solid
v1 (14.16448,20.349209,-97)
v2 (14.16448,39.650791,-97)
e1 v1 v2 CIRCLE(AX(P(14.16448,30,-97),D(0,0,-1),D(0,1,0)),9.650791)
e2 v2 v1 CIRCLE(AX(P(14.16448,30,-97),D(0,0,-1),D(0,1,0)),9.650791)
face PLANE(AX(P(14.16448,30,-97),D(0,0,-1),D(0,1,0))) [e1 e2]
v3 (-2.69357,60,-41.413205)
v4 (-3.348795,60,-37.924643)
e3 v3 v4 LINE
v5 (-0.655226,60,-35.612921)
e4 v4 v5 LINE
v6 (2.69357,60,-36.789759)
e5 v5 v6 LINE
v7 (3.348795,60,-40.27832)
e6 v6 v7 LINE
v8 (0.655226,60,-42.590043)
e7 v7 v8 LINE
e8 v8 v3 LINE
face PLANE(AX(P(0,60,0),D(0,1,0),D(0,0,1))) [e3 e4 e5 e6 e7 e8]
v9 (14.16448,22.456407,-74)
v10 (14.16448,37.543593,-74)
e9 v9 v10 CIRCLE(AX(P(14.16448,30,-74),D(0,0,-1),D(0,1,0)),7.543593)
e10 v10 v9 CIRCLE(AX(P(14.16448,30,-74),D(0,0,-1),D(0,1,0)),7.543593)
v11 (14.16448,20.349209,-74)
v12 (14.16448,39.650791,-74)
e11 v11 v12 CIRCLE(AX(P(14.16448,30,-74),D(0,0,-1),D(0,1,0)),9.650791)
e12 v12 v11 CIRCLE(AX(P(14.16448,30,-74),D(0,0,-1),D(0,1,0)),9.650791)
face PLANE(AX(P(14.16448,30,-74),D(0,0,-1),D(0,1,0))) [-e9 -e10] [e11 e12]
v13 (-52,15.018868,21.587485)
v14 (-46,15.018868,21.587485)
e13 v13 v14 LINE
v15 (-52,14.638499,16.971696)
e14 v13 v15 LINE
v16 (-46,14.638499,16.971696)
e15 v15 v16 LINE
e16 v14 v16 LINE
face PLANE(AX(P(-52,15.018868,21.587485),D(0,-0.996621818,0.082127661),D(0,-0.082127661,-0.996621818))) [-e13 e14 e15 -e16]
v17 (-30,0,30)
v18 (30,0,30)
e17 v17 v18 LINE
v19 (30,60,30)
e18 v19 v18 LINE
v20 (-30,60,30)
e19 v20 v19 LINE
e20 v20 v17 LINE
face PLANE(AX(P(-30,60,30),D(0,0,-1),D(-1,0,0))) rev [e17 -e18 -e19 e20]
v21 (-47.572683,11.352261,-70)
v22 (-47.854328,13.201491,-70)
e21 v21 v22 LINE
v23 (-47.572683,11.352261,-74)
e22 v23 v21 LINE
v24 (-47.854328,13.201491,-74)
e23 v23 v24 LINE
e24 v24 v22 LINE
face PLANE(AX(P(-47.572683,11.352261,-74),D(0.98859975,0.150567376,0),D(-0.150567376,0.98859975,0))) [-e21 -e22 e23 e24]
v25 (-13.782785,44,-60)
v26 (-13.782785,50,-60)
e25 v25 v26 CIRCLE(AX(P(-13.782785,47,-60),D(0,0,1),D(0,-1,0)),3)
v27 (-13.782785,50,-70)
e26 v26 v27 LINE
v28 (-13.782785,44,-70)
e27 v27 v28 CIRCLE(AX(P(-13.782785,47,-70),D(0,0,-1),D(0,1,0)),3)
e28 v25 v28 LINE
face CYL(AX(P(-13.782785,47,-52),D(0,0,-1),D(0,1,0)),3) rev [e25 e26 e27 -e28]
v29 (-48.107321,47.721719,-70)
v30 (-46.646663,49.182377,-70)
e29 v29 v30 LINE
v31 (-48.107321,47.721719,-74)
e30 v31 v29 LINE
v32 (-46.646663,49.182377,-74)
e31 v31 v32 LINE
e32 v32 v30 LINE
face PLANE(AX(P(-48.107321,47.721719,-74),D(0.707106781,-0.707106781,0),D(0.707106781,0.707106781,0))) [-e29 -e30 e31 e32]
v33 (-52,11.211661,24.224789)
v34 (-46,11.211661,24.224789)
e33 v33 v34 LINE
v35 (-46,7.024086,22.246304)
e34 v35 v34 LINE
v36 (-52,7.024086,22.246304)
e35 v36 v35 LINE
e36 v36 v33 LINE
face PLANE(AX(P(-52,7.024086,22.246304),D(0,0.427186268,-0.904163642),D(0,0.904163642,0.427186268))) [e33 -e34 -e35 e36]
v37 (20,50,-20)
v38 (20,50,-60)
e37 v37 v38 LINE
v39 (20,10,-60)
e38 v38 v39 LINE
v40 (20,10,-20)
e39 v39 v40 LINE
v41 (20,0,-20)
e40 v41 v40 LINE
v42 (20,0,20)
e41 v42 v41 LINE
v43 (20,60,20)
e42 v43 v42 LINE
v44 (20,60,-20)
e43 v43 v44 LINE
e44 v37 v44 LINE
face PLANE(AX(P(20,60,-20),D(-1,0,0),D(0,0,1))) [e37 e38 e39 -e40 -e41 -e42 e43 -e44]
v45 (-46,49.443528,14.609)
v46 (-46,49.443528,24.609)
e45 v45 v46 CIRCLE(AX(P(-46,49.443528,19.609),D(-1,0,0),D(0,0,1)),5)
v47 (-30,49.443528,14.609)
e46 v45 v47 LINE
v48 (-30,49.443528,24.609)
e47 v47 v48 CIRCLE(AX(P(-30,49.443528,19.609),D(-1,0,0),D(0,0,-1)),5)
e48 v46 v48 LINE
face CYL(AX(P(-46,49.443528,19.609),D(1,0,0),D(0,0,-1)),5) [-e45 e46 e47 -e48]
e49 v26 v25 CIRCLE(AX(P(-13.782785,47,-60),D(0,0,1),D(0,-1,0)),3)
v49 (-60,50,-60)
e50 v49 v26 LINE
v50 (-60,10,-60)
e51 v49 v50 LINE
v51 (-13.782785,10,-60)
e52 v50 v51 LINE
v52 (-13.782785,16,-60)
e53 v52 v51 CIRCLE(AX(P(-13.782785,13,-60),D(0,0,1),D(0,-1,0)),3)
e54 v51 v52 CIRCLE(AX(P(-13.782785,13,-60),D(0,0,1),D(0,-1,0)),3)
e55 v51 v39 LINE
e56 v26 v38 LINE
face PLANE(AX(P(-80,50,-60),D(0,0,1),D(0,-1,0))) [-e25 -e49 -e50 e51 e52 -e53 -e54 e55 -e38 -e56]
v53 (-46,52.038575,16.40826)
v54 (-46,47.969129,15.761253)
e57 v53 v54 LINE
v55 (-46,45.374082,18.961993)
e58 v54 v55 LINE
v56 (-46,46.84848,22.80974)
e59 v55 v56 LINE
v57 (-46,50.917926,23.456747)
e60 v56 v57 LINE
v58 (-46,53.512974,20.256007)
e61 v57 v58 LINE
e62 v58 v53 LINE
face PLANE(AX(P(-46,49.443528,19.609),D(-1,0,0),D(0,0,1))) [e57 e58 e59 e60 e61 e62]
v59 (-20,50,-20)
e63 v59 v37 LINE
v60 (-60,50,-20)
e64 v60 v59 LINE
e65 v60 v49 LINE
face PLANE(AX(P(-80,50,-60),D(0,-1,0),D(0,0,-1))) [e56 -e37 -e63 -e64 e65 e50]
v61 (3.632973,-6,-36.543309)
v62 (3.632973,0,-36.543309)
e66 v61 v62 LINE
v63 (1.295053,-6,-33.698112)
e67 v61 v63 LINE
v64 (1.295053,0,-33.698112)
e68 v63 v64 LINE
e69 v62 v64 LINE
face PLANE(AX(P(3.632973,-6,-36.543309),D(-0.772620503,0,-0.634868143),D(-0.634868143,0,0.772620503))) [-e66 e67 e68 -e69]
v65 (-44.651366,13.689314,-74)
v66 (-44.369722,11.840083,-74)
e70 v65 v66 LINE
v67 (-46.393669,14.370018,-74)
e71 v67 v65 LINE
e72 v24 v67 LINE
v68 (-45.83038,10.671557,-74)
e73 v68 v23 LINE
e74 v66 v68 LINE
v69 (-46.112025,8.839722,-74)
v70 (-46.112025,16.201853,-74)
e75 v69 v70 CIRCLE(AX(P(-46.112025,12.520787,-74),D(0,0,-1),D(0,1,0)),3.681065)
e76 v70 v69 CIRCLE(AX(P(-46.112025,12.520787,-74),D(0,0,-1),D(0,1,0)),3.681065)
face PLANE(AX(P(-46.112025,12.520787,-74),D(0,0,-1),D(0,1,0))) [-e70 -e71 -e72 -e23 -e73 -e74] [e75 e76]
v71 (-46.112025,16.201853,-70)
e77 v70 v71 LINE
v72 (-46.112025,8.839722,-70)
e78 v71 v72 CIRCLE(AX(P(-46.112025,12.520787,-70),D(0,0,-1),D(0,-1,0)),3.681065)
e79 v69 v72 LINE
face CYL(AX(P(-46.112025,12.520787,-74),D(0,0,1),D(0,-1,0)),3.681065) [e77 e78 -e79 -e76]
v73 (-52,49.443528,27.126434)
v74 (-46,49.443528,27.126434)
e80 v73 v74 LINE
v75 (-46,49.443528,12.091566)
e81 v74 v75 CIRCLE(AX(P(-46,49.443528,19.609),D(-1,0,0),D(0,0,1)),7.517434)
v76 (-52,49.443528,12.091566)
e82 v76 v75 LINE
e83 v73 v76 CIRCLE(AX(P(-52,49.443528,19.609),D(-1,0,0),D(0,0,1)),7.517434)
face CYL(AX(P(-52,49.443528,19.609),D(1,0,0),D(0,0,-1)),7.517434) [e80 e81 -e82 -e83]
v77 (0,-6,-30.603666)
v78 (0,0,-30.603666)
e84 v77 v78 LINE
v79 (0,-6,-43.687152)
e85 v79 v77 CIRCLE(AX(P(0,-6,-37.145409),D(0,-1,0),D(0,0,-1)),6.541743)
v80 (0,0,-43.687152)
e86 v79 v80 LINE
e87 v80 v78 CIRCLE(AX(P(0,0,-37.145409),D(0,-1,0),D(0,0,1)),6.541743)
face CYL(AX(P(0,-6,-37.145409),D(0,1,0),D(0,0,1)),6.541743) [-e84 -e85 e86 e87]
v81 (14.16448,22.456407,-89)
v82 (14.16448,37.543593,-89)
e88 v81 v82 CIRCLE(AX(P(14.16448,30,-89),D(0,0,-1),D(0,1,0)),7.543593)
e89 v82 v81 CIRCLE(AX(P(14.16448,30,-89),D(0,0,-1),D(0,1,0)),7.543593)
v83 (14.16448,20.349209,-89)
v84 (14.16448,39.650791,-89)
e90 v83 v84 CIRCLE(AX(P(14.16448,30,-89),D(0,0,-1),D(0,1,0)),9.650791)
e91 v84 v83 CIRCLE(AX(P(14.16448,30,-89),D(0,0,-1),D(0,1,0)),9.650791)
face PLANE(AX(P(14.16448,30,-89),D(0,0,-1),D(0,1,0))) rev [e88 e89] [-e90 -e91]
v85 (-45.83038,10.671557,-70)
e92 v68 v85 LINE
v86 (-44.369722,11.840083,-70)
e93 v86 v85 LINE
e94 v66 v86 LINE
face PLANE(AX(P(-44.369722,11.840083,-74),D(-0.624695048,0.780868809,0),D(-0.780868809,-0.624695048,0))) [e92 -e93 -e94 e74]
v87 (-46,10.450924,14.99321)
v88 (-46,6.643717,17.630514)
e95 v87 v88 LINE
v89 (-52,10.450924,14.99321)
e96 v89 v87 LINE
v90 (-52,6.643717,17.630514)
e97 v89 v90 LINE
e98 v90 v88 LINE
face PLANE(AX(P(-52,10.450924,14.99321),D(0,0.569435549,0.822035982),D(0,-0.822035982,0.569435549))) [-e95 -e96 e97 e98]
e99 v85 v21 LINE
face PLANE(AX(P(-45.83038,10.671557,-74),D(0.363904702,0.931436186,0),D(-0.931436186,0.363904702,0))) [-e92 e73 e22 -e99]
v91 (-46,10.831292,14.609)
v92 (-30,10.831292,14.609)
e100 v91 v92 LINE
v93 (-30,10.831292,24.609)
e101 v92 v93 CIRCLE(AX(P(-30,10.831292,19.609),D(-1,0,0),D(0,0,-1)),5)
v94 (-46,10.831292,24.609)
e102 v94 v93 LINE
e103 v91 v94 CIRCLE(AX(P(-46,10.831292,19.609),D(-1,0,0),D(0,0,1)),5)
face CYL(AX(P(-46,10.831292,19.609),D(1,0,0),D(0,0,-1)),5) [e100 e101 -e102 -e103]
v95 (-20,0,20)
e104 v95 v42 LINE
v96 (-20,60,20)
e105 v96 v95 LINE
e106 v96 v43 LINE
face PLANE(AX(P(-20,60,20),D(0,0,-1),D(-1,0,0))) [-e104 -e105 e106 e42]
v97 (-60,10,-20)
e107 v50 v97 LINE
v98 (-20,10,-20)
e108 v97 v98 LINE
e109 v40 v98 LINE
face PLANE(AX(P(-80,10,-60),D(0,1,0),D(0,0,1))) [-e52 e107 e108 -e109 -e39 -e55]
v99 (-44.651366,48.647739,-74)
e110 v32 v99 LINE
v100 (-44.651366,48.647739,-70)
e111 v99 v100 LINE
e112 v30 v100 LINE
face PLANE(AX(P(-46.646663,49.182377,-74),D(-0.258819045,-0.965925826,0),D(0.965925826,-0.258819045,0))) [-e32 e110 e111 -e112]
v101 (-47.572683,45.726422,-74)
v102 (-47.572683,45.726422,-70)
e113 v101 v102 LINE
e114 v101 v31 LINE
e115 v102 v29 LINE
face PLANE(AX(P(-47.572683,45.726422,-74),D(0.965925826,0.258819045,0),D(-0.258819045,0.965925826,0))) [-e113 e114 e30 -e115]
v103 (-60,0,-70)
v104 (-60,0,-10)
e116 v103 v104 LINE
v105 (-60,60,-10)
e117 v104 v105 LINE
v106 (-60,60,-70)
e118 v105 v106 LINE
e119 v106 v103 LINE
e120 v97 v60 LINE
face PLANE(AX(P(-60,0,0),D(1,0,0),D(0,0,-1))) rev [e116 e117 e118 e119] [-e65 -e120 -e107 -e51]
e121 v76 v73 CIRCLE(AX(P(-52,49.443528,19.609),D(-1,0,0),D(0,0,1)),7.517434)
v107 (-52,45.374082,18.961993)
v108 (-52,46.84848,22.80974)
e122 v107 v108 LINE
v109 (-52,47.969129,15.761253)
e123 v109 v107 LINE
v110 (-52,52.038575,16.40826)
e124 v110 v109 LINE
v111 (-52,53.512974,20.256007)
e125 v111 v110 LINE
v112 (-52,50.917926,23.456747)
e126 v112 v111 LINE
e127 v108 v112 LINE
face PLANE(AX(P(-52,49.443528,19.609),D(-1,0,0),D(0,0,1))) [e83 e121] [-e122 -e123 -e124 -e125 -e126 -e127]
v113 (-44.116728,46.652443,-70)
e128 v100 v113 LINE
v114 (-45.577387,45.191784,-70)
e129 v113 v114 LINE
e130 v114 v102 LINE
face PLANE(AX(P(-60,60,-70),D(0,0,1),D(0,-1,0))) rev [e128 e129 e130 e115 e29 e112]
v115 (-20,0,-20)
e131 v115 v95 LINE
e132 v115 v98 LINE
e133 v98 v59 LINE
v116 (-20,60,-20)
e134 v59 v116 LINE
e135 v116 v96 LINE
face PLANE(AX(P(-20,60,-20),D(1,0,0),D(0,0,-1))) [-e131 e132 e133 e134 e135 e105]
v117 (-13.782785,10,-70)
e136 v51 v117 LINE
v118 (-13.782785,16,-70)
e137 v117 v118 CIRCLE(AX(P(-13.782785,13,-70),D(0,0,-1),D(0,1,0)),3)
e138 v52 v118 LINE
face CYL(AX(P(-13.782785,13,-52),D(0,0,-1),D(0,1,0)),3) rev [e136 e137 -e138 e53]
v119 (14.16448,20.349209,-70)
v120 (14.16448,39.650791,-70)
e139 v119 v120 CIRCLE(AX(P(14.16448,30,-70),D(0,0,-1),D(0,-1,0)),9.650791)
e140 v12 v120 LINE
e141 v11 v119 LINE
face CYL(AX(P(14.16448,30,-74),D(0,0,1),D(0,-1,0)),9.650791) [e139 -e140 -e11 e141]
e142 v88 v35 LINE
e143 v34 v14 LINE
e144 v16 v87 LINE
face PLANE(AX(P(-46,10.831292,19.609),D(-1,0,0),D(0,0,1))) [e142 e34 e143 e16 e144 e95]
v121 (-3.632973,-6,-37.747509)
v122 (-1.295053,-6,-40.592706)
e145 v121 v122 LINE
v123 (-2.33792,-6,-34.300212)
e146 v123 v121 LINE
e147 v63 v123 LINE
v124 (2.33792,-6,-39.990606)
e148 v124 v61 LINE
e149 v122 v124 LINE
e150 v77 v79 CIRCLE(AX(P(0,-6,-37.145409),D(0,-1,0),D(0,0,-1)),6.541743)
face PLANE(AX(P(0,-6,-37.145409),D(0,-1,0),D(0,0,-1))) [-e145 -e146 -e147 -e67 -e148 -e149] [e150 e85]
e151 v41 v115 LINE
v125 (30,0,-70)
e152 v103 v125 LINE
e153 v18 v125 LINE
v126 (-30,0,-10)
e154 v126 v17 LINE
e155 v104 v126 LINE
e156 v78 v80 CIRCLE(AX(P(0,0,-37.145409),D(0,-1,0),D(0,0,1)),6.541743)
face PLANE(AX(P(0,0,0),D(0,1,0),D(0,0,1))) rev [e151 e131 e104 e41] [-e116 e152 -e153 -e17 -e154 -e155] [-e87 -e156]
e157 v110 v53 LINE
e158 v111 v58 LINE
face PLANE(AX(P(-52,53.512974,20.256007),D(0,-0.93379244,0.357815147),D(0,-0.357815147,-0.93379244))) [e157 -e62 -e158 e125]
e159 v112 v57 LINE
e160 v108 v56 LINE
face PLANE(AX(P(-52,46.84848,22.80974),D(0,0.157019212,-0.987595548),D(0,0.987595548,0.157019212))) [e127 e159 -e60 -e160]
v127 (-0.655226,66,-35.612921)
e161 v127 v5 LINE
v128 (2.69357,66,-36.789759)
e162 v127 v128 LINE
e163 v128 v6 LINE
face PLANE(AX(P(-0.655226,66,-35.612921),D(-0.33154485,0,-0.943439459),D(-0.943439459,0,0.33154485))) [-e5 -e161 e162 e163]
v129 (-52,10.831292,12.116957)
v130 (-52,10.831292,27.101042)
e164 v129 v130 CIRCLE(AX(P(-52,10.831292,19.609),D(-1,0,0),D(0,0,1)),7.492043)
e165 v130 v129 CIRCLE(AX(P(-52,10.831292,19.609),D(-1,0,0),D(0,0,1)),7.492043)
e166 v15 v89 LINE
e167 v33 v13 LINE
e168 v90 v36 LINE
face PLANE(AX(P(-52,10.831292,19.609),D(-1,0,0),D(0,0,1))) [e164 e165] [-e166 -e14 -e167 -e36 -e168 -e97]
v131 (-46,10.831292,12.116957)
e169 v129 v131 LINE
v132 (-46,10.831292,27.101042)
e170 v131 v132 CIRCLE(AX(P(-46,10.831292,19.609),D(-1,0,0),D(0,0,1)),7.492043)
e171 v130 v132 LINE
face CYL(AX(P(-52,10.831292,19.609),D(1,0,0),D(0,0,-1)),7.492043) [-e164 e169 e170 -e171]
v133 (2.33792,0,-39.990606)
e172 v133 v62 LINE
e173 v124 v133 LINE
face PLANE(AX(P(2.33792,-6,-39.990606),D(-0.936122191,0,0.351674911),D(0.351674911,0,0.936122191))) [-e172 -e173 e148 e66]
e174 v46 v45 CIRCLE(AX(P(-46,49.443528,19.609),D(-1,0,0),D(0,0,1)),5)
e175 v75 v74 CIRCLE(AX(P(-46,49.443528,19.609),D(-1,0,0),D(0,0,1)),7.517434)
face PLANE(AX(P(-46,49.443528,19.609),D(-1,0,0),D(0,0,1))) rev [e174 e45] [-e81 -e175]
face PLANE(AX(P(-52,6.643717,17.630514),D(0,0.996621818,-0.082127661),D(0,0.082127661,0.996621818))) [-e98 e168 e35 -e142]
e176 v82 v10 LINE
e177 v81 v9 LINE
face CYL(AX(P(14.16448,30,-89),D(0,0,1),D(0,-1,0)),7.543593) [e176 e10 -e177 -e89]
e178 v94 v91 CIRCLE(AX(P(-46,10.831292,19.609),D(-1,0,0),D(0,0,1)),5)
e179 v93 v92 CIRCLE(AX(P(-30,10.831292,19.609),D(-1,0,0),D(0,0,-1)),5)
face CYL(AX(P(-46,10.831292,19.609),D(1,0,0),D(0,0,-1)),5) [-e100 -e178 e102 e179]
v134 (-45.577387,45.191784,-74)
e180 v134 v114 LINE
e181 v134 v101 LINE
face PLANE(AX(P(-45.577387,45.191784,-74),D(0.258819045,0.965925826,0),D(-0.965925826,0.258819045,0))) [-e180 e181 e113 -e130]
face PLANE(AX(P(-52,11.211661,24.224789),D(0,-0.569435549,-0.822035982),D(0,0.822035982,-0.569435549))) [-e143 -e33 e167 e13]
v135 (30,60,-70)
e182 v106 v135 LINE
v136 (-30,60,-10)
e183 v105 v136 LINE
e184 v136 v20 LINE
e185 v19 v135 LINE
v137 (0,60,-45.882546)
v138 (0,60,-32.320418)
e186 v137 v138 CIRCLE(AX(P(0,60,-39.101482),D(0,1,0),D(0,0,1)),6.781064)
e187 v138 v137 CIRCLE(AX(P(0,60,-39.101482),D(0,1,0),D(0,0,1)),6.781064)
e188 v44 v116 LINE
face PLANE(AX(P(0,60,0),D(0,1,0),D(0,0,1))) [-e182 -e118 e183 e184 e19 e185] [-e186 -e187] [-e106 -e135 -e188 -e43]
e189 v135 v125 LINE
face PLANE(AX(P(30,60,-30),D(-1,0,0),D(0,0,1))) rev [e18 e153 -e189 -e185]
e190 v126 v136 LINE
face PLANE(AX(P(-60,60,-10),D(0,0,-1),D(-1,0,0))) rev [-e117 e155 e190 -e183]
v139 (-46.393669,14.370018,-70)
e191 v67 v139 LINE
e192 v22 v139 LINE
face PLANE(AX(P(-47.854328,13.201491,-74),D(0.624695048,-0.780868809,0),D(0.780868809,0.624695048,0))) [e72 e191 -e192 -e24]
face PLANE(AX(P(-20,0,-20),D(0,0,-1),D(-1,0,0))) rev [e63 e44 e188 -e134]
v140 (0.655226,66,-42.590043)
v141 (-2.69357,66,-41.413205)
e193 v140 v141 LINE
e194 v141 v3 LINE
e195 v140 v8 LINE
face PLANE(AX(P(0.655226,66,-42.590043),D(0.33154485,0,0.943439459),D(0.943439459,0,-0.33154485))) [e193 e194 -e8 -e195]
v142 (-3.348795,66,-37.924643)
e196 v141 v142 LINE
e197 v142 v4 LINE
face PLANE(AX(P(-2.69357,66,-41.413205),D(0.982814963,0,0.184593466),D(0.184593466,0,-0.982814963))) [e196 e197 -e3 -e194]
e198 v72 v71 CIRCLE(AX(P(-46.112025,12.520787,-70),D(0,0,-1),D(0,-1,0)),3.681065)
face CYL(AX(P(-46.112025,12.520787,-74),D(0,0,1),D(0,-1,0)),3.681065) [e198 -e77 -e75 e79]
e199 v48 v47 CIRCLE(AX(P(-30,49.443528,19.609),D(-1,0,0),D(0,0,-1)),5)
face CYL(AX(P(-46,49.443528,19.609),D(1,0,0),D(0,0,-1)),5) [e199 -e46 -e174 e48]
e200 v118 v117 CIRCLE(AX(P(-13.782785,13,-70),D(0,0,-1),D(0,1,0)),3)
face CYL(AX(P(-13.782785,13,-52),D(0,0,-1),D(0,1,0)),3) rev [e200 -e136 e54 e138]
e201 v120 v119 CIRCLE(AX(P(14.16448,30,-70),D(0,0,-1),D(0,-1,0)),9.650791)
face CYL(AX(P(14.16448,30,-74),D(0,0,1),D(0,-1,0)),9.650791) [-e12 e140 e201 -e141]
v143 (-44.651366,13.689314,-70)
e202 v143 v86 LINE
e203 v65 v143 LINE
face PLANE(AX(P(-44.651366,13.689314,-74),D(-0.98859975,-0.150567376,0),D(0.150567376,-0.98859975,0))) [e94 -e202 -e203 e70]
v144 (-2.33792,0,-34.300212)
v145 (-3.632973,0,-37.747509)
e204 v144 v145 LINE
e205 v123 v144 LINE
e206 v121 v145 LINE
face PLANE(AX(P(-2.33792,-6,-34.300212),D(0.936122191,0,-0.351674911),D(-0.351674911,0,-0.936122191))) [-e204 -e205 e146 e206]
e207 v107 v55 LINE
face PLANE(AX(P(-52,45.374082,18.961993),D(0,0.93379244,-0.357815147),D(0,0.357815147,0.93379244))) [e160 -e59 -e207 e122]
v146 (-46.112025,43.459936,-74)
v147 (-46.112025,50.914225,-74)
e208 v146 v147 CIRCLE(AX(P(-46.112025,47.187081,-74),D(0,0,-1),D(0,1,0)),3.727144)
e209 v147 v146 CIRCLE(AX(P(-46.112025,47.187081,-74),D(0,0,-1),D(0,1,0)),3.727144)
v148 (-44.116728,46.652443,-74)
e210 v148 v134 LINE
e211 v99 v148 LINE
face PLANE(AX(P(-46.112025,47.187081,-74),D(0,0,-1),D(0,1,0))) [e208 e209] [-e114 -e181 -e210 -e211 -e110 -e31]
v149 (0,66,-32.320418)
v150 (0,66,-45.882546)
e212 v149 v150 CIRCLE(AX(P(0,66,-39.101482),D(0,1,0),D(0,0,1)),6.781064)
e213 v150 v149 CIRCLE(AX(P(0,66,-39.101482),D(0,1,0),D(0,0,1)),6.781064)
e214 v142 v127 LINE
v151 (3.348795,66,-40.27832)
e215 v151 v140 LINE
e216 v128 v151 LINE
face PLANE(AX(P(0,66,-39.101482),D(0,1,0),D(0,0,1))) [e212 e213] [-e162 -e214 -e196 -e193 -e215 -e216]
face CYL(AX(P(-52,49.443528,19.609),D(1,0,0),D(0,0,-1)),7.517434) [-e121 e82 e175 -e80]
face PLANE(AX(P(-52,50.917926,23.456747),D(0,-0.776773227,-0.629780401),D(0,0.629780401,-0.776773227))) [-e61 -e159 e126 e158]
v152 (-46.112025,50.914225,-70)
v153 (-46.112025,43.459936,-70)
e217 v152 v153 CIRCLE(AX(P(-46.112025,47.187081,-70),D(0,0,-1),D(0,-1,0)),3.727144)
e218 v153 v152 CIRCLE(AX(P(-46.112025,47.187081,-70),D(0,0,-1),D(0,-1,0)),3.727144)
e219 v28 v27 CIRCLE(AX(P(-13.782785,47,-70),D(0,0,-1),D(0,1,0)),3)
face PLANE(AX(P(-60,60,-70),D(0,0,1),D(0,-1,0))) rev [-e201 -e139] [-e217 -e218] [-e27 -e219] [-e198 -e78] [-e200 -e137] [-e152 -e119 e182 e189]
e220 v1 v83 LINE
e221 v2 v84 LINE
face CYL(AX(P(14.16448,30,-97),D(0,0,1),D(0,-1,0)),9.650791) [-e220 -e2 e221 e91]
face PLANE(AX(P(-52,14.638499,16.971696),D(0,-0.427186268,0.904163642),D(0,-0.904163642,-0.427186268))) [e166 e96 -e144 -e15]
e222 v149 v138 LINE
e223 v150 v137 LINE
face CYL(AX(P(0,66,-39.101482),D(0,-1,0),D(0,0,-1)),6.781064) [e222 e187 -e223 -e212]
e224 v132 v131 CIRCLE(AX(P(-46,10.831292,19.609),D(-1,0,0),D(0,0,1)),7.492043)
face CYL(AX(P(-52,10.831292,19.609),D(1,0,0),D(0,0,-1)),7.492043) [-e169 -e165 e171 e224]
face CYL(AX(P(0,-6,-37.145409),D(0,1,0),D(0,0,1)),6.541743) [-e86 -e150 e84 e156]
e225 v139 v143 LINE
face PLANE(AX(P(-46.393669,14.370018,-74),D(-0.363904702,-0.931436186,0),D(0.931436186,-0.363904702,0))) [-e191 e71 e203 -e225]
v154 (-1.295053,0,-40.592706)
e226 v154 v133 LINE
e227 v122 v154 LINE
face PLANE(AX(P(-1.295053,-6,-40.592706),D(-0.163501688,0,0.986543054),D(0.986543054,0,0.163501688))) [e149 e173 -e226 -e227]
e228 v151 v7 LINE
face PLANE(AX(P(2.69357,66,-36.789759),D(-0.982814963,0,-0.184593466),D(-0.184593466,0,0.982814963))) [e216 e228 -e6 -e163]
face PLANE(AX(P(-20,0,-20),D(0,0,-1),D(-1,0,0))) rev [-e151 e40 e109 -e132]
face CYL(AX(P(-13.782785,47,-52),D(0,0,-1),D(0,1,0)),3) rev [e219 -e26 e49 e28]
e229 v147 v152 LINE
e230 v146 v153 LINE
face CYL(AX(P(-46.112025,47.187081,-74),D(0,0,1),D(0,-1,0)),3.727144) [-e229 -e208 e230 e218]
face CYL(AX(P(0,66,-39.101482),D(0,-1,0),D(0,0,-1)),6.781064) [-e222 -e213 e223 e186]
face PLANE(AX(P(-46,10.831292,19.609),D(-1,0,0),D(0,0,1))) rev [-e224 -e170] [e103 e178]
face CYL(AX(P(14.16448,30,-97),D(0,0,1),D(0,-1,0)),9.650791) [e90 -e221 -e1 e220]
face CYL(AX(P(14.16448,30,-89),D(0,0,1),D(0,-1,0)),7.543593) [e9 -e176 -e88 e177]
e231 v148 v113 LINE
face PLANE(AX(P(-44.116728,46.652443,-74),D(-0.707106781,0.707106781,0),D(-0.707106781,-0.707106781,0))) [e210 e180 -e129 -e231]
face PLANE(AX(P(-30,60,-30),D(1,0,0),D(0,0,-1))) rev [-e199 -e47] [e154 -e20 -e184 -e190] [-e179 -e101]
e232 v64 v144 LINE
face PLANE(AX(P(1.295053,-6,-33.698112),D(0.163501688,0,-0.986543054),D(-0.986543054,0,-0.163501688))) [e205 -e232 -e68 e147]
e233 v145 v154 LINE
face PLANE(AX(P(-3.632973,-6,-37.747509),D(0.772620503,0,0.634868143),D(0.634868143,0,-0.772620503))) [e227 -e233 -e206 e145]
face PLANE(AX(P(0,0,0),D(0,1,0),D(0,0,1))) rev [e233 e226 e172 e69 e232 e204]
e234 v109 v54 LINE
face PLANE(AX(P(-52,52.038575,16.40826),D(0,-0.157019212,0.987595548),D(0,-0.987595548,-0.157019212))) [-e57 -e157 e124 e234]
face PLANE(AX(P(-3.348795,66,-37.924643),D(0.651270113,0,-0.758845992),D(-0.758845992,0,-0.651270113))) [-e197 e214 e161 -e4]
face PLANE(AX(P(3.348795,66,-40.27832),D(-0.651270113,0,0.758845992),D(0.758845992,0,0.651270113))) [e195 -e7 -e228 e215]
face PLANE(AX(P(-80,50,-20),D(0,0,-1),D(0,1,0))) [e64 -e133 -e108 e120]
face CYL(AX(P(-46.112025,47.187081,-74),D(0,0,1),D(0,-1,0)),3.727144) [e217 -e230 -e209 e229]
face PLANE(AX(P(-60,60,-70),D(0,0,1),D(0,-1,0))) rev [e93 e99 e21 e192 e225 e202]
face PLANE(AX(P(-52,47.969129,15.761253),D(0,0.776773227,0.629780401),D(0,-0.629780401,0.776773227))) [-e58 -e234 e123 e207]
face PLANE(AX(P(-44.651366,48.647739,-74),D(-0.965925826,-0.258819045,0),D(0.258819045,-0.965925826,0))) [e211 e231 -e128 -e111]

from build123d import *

# Parameters (mm, degrees)
SKETCH1_W                = 60
SKETCH1_H                = 60
SKETCH1_W_2              = 40
SKETCH1_H_2              = 40
BOSS_EXTRUDE1_DEPTH      = 60
BOSS_EXTRUDE2_DEPTH      = 30
BOSS_EXTRUDE2_DEPTH_BACK = 60
CUT_EXTRUDE1_DEPTH       = 50
CUT_EXTRUDE1_DEPTH_BACK  = 50
SKETCH3_W                = 40
SKETCH3_H                = 40
SKETCH4_W                = 40
SKETCH4_H                = 10
CUT_EXTRUDE2_DEPTH       = 60
SKETCH5_R                = 9.65079084
BOSS_EXTRUDE3_DEPTH      = 4
SKETCH6_R                = 7.543593384
BOSS_EXTRUDE4_DEPTH      = 15
SKETCH7_R                = 9.65079084
BOSS_EXTRUDE5_DEPTH      = 8
SKETCH8_R                = 3
CUT_EXTRUDE3_DEPTH       = 18
SKETCH9_R                = 3.727144442
SKETCH9_R_2              = 3.681065336
BOSS_EXTRUDE6_DEPTH      = 4
SKETCH10_R               = 6.781063786
BOSS_EXTRUDE7_DEPTH      = 6
SKETCH11_R               = 6.541743029
BOSS_EXTRUDE8_DEPTH      = 6
SKETCH12_R               = 5
BOSS_EXTRUDE9_DEPTH      = 16
SKETCH13_R               = 7.492042748
SKETCH13_R_2             = 7.517434031
BOSS_EXTRUDE10_DEPTH     = 6


with BuildPart() as part:
    # Sketch1 → Boss-Extrude1 (new body)
    with BuildSketch(Plane(origin=(0, 0, 0), x_dir=(1, 0, 0), z_dir=(0, 1, 0))):
        Rectangle(SKETCH1_W, SKETCH1_H)
        Rectangle(SKETCH1_W_2, SKETCH1_H_2, mode=Mode.SUBTRACT)
    extrude(amount=BOSS_EXTRUDE1_DEPTH)

    # Sketch2 → Boss-Extrude2 (add, two sides: drawn at the far end of the back side and taken through both)
    with BuildSketch(Plane.ZY.offset(30).offset(-BOSS_EXTRUDE2_DEPTH_BACK)):
        Polygon((-30, 60), (-70, 60), (-70, 0), (-30, 0), (-10, 0), (-10, 60), align=None)
    extrude(amount=BOSS_EXTRUDE2_DEPTH + BOSS_EXTRUDE2_DEPTH_BACK)

    # Sketch3 → Cut-Extrude1 (cut, two sides: drawn at the far end of the back side and taken through both)
    with BuildSketch(Plane.ZY.offset(30).offset(-CUT_EXTRUDE1_DEPTH_BACK)):
        with Locations((-40, 30)):
            Rectangle(SKETCH3_W, SKETCH3_H)
    extrude(amount=CUT_EXTRUDE1_DEPTH + CUT_EXTRUDE1_DEPTH_BACK, mode=Mode.SUBTRACT)

    # Sketch4 → Cut-Extrude2 (cut)
    with BuildSketch(Plane(origin=(0, 60, 0), x_dir=(1, 0, 0), z_dir=(0, 1, 0))):
        with Locations((0, 15)):
            Rectangle(SKETCH4_W, SKETCH4_H)
    extrude(amount=-CUT_EXTRUDE2_DEPTH, mode=Mode.SUBTRACT)

    # Sketch5 → Boss-Extrude3 (add)
    with BuildSketch(Plane(origin=(0, 0, -70), x_dir=(-1, 0, 0), z_dir=(0, 0, -1))):
        with Locations(Location((-14.164480052, 30, 0), (0, 0, 270))):
            Circle(SKETCH5_R)
    extrude(amount=BOSS_EXTRUDE3_DEPTH)

    # Sketch6 → Boss-Extrude4 (add)
    with BuildSketch(Plane(origin=(0, 0, -74), x_dir=(-1, 0, 0), z_dir=(0, 0, -1))):
        with Locations(Location((-14.164480052, 30, 0), (0, 0, 90))):
            Circle(SKETCH6_R)
    extrude(amount=BOSS_EXTRUDE4_DEPTH)

    # Sketch7 → Boss-Extrude5 (add)
    with BuildSketch(Plane(origin=(0, 0, -89), x_dir=(-1, 0, 0), z_dir=(0, 0, -1))):
        with Locations(Location((-14.164480052, 30, 0), (0, 0, 270))):
            Circle(SKETCH7_R)
    extrude(amount=BOSS_EXTRUDE5_DEPTH)

    # Sketch8 → Cut-Extrude3 (cut)
    with BuildSketch(Plane(origin=(0, 0, -70), x_dir=(-1, 0, 0), z_dir=(0, 0, -1))):
        with Locations(Location((13.782784639, 47, 0), (0, 0, 90))):
            Circle(SKETCH8_R)
        with Locations(Location((13.782784639, 13, 0), (0, 0, 90))):
            Circle(SKETCH8_R)
    extrude(amount=-CUT_EXTRUDE3_DEPTH, mode=Mode.SUBTRACT)

    # Sketch9 → Boss-Extrude6 (add)
    # profile 1 of 2: a face of its own
    with BuildSketch(Plane(origin=(0, 0, -70), x_dir=(-1, 0, 0), z_dir=(0, 0, -1))):
        with Locations(Location((46.11202463, 47.187080899, 0), (0, 0, 270))):
            Circle(SKETCH9_R)
        Polygon((47.572683063, 45.726422466), (48.107321156, 47.721718992), (46.646662723, 49.182377425), (44.651366197, 48.647739332), (44.116728104, 46.652442806), (45.577386537, 45.191784373), align=None, mode=Mode.SUBTRACT)
    # profile 2 of 2: a face of its own
    with BuildSketch(Plane(origin=(0, 0, -70), x_dir=(-1, 0, 0), z_dir=(0, 0, -1))):
        with Locations(Location((46.11202463, 12.520787414, 0), (0, 0, 270))):
            Circle(SKETCH9_R_2)
        Polygon((47.572683063, 11.352260668), (47.854327694, 13.201491351), (46.393669261, 14.370018097), (44.651366197, 13.689314161), (44.369721566, 11.840083478), (45.830379999, 10.671556732), align=None, mode=Mode.SUBTRACT)
    extrude(amount=BOSS_EXTRUDE6_DEPTH)

    # Sketch10 → Boss-Extrude7 (add)
    with BuildSketch(Plane(origin=(0, 60, 0), x_dir=(1, 0, 0), z_dir=(0, 1, 0))):
        with Locations(Location((0, 39.10148189, 0), (0, 0, 270))):
            Circle(SKETCH10_R)
        Polygon((2.69356978, 36.789759205), (3.348795461, 40.278320404), (0.655225682, 42.590043088), (-2.69356978, 41.413204575), (-3.348795461, 37.924643376), (-0.655225682, 35.612920692), align=None, mode=Mode.SUBTRACT)
    extrude(amount=BOSS_EXTRUDE7_DEPTH)

    # Sketch11 → Boss-Extrude8 (add)
    with BuildSketch(Plane.XZ):
        with Locations(Location((0, -37.145408849, 0), (0, 0, 90))):
            Circle(SKETCH11_R)
        Polygon((2.337920136, -39.990606), (3.632973079, -36.543309195), (1.295052943, -33.698112044), (-2.337920136, -34.300211699), (-3.632973079, -37.747508503), (-1.295052943, -40.592705654), align=None, mode=Mode.SUBTRACT)
    extrude(amount=BOSS_EXTRUDE8_DEPTH)

    # Sketch12 → Boss-Extrude9 (add)
    with BuildSketch(Plane.ZY.offset(30)):
        with Locations(Location((19.608999651, 49.443527686, 0), (0, 0, 180))):
            Circle(SKETCH12_R)
        with Locations(Location((19.608999651, 10.831292493, 0), (0, 0, 180))):
            Circle(SKETCH12_R)
    extrude(amount=BOSS_EXTRUDE9_DEPTH)

    # Sketch13 → Boss-Extrude10 (add)
    # profile 1 of 2: a face of its own
    with BuildSketch(Plane.ZY.offset(46)):
        with Locations((19.608999651, 10.831292493)):
            Circle(SKETCH13_R)
        Polygon((22.246303592, 7.024085978), (24.224789181, 11.211661446), (21.58748524, 15.018867961), (16.971695711, 14.638499008), (14.993210122, 10.45092354), (17.630514063, 6.643717026), align=None, mode=Mode.SUBTRACT)
    # profile 2 of 2: a face of its own
    with BuildSketch(Plane.ZY.offset(46)):
        with Locations((19.608999651, 49.443527686)):
            Circle(SKETCH13_R_2)
        Polygon((22.809739777, 46.848480214), (23.456746749, 50.91792621), (20.256006623, 53.512973682), (16.408259526, 52.038575158), (15.761252554, 47.969129162), (18.96199268, 45.37408169), align=None, mode=Mode.SUBTRACT)
    extrude(amount=BOSS_EXTRUDE10_DEPTH)


solid = part.part
